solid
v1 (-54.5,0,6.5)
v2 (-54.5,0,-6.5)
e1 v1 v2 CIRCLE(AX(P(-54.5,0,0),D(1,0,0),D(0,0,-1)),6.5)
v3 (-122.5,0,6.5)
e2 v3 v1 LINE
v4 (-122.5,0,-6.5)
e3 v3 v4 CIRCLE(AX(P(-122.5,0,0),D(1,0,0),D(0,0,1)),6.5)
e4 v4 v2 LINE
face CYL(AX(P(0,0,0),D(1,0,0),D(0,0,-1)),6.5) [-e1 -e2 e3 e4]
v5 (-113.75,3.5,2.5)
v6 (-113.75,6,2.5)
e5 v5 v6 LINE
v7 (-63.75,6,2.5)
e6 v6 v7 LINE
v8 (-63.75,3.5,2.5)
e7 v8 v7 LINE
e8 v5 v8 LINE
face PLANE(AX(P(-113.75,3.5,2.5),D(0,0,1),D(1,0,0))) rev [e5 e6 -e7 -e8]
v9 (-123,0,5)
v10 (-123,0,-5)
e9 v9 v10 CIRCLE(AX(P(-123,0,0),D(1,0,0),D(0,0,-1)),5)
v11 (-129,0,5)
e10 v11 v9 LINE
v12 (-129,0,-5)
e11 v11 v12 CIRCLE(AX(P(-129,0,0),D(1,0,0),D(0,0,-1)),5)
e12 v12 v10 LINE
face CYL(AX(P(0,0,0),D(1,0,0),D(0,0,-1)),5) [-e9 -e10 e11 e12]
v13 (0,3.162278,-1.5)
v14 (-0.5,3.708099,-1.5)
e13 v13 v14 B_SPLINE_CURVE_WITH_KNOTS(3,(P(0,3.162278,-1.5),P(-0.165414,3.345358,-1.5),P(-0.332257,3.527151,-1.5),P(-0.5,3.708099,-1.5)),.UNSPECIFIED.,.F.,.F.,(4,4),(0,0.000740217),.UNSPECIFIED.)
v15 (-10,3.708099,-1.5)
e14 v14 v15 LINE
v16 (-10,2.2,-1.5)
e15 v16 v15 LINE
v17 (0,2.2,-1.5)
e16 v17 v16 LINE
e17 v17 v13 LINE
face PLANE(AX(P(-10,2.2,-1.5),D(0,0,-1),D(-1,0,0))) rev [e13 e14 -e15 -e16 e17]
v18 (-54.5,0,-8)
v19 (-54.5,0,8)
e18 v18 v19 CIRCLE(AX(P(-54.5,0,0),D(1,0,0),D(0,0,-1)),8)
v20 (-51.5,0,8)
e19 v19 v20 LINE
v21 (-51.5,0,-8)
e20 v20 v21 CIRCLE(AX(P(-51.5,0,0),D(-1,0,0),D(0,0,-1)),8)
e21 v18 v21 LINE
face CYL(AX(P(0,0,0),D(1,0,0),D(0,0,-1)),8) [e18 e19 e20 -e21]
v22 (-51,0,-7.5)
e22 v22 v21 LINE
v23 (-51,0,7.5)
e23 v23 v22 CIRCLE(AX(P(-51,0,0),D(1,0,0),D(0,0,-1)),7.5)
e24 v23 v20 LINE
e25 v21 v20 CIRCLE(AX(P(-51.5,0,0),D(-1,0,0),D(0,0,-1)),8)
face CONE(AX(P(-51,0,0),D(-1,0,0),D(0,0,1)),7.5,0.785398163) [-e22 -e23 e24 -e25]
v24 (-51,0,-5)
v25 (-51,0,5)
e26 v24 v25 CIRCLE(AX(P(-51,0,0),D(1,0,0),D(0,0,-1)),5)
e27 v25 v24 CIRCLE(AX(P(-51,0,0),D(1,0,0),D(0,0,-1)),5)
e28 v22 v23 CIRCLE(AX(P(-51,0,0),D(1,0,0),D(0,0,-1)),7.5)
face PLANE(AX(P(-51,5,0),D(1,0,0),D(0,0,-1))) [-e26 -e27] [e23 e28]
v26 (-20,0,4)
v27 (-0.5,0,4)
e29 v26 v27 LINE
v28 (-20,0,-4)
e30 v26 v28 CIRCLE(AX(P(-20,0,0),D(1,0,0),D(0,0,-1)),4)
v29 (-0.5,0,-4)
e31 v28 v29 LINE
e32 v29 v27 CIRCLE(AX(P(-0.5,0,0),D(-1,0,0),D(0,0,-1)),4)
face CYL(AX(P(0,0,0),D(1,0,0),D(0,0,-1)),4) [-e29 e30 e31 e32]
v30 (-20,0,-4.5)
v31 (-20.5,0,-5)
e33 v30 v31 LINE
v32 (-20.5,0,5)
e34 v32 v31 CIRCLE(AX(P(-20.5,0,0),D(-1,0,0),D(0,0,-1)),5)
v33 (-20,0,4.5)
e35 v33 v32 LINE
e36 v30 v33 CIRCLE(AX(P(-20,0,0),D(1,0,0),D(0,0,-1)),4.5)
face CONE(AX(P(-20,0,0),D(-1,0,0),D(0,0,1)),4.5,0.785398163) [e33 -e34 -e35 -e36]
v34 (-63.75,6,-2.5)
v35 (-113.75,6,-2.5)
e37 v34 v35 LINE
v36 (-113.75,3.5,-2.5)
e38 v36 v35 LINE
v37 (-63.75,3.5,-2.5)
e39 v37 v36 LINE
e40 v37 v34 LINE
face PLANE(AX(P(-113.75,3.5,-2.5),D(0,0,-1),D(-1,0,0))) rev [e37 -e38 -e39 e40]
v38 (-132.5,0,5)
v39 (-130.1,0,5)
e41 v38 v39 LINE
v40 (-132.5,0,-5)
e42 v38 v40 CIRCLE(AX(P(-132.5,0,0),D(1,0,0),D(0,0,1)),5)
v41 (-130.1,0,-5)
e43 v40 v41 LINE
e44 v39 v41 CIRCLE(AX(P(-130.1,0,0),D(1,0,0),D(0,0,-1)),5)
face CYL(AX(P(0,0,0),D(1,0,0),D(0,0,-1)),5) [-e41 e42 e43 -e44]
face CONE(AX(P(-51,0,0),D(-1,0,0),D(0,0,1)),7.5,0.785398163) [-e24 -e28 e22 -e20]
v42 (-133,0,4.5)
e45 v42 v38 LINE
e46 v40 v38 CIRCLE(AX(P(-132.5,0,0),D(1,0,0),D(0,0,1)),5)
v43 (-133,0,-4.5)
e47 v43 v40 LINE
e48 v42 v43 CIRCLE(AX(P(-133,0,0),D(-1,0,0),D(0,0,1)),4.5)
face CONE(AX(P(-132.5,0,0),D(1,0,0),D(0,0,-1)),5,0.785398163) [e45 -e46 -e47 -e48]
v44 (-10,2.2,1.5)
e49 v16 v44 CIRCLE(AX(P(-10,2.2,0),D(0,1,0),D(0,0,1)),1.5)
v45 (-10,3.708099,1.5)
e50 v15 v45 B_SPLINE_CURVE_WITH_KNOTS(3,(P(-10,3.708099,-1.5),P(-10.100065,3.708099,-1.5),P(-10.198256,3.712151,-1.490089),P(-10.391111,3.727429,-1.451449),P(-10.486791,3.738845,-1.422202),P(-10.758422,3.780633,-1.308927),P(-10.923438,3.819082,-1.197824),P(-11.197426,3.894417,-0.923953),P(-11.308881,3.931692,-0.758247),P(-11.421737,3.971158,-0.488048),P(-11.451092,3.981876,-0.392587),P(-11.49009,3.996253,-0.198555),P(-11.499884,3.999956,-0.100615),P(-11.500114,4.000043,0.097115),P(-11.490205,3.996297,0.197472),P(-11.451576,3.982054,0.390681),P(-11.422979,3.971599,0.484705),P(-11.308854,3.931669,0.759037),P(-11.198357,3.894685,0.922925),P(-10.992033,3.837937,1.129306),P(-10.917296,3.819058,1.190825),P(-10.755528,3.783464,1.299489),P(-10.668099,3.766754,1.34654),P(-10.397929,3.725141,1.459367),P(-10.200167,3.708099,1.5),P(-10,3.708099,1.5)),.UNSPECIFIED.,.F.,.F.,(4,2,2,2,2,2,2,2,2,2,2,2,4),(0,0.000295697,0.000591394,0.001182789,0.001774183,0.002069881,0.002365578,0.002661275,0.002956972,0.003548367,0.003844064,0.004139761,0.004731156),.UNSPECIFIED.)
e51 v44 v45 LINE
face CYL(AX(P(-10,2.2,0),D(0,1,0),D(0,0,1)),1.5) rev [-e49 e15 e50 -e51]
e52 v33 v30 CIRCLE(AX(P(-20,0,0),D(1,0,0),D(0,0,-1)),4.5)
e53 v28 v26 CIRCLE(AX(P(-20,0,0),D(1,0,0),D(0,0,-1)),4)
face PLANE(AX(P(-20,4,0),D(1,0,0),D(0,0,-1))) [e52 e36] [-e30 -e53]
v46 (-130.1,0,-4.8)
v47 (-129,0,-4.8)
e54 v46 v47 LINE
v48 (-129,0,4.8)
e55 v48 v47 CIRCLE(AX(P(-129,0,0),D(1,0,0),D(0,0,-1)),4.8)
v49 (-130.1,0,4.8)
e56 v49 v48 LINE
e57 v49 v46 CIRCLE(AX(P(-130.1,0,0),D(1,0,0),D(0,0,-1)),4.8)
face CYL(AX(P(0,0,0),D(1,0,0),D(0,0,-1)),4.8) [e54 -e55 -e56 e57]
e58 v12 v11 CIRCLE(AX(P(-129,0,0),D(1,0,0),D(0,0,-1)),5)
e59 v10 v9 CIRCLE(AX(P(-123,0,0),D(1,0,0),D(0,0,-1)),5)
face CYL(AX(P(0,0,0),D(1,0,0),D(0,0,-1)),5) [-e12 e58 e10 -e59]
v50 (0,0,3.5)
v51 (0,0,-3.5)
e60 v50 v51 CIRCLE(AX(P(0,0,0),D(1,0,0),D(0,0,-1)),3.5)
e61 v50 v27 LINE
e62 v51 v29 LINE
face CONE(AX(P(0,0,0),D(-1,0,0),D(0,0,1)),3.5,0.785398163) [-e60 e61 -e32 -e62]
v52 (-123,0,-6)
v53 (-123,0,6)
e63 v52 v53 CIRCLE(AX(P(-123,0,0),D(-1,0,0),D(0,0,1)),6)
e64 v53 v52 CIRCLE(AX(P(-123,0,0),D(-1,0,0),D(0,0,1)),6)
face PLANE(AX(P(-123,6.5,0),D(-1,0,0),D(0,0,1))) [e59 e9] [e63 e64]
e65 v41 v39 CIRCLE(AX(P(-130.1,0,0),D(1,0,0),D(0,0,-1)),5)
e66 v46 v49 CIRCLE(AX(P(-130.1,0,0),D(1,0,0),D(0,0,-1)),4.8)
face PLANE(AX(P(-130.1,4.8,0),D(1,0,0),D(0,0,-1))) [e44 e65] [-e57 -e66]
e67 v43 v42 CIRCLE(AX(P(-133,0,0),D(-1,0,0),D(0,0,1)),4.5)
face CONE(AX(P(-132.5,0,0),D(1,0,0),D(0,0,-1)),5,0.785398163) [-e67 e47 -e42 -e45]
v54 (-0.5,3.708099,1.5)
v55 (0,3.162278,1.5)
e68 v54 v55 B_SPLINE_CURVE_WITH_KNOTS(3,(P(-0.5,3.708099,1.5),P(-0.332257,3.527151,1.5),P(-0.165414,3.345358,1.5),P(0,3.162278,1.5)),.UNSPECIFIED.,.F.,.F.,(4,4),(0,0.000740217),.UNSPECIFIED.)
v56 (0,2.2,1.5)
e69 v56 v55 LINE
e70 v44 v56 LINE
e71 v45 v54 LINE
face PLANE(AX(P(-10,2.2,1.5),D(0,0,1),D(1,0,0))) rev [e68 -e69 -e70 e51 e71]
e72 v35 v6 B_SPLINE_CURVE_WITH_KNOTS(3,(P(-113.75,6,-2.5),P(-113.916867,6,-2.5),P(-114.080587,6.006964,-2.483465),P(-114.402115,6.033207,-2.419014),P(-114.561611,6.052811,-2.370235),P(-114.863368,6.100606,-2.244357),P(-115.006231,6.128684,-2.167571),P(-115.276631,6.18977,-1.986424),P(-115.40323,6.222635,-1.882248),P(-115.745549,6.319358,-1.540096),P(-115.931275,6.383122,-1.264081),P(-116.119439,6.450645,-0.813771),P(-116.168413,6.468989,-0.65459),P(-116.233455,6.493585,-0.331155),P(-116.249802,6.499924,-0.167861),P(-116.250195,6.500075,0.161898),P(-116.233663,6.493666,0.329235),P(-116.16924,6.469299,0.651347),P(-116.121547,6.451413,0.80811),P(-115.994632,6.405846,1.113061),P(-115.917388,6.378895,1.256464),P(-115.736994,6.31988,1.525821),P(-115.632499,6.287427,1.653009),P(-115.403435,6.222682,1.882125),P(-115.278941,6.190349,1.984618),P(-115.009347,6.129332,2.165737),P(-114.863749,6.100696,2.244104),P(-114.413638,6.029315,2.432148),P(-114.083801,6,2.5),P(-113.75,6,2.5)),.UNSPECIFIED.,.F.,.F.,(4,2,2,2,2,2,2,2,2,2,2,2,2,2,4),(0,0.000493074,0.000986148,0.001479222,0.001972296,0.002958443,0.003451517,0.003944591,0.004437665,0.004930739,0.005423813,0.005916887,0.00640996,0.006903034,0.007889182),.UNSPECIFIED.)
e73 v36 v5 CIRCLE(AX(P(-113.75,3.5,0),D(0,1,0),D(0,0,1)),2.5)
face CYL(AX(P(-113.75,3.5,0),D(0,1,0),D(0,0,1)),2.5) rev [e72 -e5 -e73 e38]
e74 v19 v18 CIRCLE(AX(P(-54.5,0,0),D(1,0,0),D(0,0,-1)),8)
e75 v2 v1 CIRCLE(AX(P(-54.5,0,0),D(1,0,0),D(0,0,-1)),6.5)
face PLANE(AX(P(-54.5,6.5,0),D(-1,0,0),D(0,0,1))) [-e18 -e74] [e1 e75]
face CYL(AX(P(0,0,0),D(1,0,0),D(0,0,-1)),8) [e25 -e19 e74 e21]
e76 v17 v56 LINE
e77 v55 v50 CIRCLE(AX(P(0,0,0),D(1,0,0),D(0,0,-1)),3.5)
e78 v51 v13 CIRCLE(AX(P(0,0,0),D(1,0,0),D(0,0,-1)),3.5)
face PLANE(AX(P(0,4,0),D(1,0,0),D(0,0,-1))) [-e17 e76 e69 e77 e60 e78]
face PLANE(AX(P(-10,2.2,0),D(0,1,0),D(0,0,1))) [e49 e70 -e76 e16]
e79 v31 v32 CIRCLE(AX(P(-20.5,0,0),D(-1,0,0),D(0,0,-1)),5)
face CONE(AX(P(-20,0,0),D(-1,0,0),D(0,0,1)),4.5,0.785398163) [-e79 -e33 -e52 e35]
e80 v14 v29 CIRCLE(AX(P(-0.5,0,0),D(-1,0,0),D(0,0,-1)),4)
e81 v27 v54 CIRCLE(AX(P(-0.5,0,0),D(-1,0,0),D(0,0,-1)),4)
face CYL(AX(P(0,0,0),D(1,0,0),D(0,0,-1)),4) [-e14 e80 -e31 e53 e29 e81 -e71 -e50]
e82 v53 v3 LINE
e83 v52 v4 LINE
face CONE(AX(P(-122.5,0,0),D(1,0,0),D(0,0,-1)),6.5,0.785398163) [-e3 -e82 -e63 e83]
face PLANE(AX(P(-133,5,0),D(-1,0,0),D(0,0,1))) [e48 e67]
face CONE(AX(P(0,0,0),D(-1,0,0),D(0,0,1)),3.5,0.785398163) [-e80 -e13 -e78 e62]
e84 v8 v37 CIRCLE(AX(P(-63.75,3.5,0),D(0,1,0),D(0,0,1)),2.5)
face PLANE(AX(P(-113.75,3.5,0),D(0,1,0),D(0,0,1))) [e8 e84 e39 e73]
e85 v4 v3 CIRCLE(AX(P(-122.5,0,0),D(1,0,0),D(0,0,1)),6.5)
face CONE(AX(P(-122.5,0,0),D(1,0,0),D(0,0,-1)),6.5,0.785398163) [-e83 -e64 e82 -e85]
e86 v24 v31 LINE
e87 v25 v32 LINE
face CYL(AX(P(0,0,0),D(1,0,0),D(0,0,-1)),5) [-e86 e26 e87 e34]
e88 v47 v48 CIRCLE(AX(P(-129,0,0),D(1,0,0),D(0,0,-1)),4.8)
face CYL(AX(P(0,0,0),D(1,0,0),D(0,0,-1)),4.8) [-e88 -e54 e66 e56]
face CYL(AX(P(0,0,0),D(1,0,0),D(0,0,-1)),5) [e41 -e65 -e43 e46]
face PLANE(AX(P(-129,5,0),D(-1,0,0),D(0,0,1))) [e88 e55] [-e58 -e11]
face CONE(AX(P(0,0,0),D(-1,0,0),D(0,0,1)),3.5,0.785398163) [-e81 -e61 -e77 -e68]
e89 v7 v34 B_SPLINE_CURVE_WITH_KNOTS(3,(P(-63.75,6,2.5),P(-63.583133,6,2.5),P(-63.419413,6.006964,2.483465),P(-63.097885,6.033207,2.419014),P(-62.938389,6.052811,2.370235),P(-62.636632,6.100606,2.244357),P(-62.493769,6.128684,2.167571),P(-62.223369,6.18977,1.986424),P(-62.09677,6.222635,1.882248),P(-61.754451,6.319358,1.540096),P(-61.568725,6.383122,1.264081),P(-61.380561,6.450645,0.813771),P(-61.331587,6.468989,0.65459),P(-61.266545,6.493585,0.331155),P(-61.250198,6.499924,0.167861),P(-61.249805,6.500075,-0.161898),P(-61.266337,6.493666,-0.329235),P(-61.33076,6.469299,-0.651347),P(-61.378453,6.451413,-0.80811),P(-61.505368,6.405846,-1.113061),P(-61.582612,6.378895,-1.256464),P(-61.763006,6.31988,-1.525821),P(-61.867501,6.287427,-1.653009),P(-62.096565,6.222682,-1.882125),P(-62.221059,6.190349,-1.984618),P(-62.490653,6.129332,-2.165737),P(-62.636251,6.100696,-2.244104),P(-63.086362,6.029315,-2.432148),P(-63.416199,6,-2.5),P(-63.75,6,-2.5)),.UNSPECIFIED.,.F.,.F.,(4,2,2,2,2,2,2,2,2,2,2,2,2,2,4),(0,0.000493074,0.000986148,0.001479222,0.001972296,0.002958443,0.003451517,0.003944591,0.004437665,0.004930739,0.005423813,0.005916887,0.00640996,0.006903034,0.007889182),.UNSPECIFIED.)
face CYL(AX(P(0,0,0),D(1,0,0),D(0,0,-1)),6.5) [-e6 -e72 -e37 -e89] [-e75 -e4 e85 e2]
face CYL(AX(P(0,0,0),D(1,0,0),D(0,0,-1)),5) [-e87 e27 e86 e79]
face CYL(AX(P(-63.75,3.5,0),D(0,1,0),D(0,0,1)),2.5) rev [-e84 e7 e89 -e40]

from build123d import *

# Parameters (mm, degrees)
CUT_EXTRUDE_START   = 4
CUT_EXTRUDE_1_DEPTH = 1.8
CHAMFER_1_SIZE      = 0.5
CUT_EXTRUDE_3_DEPTH = 3


with BuildPart() as part:
    # 草图1 → 旋转1 (revolve)
    with BuildSketch(Plane.XY, mode=Mode.PRIVATE) as revolve_1_sk:
        Polygon((-133, 5), (-130.1, 5), (-130.1, 4.8), (-129, 4.8), (-129, 5), (-123, 5), (-123, 6.5), (-54.5, 6.5), (-54.5, 8), (-51, 8), (-51, 5), (-20, 5), (-20, 4), (0, 4), (0, 0), (-133, 0), align=None)
    revolve(revolve_1_sk.sketch.rotate(Axis((0, 0, 0), (-1, 0, 0)), 90), axis=Axis((0, 0, 0), (-1, 0, 0)))

    # 草图2 → 切除-拉伸1 (cut)
    with BuildSketch(Plane(origin=(0, 0, 0), x_dir=(1, 0, 0), z_dir=(0, 1, 0)).offset(CUT_EXTRUDE_START)):
        with BuildLine():
            Line((-10, 1.5), (0, 1.5))
            ThreePointArc((0, 1.5), (1.5, 0), (0, -1.5))
            Line((0, -1.5), (-10, -1.5))
            ThreePointArc((-10, -1.5), (-11.5, 0), (-10, 1.5))
        make_face()
    extrude(amount=-CUT_EXTRUDE_1_DEPTH, mode=Mode.SUBTRACT)

    # 倒角1
    chamfer_1_edges = [part.edges().sort_by_distance(p)[0] for p in [
        (-20, 0, 5),
        (-51, 0, 8),
        (-123, 0, 6.5),
        (-133, 0, 5),
        (0, -3.31662479, 2.236067977),
    ]]
    chamfer(chamfer_1_edges, length=CHAMFER_1_SIZE)

    # 草图4 → 切除-拉伸3 (cut)
    with BuildSketch(Plane(origin=(0, 6.5, 0), x_dir=(1, 0, 0), z_dir=(0, 1, 0))):
        with BuildLine():
            Line((-113.75, 2.5), (-63.75, 2.5))
            ThreePointArc((-63.75, 2.5), (-61.25, 0), (-63.75, -2.5))
            Line((-63.75, -2.5), (-113.75, -2.5))
            ThreePointArc((-113.75, -2.5), (-116.25, 0), (-113.75, 2.5))
        make_face()
    extrude(amount=-CUT_EXTRUDE_3_DEPTH, mode=Mode.SUBTRACT)


solid = part.part
